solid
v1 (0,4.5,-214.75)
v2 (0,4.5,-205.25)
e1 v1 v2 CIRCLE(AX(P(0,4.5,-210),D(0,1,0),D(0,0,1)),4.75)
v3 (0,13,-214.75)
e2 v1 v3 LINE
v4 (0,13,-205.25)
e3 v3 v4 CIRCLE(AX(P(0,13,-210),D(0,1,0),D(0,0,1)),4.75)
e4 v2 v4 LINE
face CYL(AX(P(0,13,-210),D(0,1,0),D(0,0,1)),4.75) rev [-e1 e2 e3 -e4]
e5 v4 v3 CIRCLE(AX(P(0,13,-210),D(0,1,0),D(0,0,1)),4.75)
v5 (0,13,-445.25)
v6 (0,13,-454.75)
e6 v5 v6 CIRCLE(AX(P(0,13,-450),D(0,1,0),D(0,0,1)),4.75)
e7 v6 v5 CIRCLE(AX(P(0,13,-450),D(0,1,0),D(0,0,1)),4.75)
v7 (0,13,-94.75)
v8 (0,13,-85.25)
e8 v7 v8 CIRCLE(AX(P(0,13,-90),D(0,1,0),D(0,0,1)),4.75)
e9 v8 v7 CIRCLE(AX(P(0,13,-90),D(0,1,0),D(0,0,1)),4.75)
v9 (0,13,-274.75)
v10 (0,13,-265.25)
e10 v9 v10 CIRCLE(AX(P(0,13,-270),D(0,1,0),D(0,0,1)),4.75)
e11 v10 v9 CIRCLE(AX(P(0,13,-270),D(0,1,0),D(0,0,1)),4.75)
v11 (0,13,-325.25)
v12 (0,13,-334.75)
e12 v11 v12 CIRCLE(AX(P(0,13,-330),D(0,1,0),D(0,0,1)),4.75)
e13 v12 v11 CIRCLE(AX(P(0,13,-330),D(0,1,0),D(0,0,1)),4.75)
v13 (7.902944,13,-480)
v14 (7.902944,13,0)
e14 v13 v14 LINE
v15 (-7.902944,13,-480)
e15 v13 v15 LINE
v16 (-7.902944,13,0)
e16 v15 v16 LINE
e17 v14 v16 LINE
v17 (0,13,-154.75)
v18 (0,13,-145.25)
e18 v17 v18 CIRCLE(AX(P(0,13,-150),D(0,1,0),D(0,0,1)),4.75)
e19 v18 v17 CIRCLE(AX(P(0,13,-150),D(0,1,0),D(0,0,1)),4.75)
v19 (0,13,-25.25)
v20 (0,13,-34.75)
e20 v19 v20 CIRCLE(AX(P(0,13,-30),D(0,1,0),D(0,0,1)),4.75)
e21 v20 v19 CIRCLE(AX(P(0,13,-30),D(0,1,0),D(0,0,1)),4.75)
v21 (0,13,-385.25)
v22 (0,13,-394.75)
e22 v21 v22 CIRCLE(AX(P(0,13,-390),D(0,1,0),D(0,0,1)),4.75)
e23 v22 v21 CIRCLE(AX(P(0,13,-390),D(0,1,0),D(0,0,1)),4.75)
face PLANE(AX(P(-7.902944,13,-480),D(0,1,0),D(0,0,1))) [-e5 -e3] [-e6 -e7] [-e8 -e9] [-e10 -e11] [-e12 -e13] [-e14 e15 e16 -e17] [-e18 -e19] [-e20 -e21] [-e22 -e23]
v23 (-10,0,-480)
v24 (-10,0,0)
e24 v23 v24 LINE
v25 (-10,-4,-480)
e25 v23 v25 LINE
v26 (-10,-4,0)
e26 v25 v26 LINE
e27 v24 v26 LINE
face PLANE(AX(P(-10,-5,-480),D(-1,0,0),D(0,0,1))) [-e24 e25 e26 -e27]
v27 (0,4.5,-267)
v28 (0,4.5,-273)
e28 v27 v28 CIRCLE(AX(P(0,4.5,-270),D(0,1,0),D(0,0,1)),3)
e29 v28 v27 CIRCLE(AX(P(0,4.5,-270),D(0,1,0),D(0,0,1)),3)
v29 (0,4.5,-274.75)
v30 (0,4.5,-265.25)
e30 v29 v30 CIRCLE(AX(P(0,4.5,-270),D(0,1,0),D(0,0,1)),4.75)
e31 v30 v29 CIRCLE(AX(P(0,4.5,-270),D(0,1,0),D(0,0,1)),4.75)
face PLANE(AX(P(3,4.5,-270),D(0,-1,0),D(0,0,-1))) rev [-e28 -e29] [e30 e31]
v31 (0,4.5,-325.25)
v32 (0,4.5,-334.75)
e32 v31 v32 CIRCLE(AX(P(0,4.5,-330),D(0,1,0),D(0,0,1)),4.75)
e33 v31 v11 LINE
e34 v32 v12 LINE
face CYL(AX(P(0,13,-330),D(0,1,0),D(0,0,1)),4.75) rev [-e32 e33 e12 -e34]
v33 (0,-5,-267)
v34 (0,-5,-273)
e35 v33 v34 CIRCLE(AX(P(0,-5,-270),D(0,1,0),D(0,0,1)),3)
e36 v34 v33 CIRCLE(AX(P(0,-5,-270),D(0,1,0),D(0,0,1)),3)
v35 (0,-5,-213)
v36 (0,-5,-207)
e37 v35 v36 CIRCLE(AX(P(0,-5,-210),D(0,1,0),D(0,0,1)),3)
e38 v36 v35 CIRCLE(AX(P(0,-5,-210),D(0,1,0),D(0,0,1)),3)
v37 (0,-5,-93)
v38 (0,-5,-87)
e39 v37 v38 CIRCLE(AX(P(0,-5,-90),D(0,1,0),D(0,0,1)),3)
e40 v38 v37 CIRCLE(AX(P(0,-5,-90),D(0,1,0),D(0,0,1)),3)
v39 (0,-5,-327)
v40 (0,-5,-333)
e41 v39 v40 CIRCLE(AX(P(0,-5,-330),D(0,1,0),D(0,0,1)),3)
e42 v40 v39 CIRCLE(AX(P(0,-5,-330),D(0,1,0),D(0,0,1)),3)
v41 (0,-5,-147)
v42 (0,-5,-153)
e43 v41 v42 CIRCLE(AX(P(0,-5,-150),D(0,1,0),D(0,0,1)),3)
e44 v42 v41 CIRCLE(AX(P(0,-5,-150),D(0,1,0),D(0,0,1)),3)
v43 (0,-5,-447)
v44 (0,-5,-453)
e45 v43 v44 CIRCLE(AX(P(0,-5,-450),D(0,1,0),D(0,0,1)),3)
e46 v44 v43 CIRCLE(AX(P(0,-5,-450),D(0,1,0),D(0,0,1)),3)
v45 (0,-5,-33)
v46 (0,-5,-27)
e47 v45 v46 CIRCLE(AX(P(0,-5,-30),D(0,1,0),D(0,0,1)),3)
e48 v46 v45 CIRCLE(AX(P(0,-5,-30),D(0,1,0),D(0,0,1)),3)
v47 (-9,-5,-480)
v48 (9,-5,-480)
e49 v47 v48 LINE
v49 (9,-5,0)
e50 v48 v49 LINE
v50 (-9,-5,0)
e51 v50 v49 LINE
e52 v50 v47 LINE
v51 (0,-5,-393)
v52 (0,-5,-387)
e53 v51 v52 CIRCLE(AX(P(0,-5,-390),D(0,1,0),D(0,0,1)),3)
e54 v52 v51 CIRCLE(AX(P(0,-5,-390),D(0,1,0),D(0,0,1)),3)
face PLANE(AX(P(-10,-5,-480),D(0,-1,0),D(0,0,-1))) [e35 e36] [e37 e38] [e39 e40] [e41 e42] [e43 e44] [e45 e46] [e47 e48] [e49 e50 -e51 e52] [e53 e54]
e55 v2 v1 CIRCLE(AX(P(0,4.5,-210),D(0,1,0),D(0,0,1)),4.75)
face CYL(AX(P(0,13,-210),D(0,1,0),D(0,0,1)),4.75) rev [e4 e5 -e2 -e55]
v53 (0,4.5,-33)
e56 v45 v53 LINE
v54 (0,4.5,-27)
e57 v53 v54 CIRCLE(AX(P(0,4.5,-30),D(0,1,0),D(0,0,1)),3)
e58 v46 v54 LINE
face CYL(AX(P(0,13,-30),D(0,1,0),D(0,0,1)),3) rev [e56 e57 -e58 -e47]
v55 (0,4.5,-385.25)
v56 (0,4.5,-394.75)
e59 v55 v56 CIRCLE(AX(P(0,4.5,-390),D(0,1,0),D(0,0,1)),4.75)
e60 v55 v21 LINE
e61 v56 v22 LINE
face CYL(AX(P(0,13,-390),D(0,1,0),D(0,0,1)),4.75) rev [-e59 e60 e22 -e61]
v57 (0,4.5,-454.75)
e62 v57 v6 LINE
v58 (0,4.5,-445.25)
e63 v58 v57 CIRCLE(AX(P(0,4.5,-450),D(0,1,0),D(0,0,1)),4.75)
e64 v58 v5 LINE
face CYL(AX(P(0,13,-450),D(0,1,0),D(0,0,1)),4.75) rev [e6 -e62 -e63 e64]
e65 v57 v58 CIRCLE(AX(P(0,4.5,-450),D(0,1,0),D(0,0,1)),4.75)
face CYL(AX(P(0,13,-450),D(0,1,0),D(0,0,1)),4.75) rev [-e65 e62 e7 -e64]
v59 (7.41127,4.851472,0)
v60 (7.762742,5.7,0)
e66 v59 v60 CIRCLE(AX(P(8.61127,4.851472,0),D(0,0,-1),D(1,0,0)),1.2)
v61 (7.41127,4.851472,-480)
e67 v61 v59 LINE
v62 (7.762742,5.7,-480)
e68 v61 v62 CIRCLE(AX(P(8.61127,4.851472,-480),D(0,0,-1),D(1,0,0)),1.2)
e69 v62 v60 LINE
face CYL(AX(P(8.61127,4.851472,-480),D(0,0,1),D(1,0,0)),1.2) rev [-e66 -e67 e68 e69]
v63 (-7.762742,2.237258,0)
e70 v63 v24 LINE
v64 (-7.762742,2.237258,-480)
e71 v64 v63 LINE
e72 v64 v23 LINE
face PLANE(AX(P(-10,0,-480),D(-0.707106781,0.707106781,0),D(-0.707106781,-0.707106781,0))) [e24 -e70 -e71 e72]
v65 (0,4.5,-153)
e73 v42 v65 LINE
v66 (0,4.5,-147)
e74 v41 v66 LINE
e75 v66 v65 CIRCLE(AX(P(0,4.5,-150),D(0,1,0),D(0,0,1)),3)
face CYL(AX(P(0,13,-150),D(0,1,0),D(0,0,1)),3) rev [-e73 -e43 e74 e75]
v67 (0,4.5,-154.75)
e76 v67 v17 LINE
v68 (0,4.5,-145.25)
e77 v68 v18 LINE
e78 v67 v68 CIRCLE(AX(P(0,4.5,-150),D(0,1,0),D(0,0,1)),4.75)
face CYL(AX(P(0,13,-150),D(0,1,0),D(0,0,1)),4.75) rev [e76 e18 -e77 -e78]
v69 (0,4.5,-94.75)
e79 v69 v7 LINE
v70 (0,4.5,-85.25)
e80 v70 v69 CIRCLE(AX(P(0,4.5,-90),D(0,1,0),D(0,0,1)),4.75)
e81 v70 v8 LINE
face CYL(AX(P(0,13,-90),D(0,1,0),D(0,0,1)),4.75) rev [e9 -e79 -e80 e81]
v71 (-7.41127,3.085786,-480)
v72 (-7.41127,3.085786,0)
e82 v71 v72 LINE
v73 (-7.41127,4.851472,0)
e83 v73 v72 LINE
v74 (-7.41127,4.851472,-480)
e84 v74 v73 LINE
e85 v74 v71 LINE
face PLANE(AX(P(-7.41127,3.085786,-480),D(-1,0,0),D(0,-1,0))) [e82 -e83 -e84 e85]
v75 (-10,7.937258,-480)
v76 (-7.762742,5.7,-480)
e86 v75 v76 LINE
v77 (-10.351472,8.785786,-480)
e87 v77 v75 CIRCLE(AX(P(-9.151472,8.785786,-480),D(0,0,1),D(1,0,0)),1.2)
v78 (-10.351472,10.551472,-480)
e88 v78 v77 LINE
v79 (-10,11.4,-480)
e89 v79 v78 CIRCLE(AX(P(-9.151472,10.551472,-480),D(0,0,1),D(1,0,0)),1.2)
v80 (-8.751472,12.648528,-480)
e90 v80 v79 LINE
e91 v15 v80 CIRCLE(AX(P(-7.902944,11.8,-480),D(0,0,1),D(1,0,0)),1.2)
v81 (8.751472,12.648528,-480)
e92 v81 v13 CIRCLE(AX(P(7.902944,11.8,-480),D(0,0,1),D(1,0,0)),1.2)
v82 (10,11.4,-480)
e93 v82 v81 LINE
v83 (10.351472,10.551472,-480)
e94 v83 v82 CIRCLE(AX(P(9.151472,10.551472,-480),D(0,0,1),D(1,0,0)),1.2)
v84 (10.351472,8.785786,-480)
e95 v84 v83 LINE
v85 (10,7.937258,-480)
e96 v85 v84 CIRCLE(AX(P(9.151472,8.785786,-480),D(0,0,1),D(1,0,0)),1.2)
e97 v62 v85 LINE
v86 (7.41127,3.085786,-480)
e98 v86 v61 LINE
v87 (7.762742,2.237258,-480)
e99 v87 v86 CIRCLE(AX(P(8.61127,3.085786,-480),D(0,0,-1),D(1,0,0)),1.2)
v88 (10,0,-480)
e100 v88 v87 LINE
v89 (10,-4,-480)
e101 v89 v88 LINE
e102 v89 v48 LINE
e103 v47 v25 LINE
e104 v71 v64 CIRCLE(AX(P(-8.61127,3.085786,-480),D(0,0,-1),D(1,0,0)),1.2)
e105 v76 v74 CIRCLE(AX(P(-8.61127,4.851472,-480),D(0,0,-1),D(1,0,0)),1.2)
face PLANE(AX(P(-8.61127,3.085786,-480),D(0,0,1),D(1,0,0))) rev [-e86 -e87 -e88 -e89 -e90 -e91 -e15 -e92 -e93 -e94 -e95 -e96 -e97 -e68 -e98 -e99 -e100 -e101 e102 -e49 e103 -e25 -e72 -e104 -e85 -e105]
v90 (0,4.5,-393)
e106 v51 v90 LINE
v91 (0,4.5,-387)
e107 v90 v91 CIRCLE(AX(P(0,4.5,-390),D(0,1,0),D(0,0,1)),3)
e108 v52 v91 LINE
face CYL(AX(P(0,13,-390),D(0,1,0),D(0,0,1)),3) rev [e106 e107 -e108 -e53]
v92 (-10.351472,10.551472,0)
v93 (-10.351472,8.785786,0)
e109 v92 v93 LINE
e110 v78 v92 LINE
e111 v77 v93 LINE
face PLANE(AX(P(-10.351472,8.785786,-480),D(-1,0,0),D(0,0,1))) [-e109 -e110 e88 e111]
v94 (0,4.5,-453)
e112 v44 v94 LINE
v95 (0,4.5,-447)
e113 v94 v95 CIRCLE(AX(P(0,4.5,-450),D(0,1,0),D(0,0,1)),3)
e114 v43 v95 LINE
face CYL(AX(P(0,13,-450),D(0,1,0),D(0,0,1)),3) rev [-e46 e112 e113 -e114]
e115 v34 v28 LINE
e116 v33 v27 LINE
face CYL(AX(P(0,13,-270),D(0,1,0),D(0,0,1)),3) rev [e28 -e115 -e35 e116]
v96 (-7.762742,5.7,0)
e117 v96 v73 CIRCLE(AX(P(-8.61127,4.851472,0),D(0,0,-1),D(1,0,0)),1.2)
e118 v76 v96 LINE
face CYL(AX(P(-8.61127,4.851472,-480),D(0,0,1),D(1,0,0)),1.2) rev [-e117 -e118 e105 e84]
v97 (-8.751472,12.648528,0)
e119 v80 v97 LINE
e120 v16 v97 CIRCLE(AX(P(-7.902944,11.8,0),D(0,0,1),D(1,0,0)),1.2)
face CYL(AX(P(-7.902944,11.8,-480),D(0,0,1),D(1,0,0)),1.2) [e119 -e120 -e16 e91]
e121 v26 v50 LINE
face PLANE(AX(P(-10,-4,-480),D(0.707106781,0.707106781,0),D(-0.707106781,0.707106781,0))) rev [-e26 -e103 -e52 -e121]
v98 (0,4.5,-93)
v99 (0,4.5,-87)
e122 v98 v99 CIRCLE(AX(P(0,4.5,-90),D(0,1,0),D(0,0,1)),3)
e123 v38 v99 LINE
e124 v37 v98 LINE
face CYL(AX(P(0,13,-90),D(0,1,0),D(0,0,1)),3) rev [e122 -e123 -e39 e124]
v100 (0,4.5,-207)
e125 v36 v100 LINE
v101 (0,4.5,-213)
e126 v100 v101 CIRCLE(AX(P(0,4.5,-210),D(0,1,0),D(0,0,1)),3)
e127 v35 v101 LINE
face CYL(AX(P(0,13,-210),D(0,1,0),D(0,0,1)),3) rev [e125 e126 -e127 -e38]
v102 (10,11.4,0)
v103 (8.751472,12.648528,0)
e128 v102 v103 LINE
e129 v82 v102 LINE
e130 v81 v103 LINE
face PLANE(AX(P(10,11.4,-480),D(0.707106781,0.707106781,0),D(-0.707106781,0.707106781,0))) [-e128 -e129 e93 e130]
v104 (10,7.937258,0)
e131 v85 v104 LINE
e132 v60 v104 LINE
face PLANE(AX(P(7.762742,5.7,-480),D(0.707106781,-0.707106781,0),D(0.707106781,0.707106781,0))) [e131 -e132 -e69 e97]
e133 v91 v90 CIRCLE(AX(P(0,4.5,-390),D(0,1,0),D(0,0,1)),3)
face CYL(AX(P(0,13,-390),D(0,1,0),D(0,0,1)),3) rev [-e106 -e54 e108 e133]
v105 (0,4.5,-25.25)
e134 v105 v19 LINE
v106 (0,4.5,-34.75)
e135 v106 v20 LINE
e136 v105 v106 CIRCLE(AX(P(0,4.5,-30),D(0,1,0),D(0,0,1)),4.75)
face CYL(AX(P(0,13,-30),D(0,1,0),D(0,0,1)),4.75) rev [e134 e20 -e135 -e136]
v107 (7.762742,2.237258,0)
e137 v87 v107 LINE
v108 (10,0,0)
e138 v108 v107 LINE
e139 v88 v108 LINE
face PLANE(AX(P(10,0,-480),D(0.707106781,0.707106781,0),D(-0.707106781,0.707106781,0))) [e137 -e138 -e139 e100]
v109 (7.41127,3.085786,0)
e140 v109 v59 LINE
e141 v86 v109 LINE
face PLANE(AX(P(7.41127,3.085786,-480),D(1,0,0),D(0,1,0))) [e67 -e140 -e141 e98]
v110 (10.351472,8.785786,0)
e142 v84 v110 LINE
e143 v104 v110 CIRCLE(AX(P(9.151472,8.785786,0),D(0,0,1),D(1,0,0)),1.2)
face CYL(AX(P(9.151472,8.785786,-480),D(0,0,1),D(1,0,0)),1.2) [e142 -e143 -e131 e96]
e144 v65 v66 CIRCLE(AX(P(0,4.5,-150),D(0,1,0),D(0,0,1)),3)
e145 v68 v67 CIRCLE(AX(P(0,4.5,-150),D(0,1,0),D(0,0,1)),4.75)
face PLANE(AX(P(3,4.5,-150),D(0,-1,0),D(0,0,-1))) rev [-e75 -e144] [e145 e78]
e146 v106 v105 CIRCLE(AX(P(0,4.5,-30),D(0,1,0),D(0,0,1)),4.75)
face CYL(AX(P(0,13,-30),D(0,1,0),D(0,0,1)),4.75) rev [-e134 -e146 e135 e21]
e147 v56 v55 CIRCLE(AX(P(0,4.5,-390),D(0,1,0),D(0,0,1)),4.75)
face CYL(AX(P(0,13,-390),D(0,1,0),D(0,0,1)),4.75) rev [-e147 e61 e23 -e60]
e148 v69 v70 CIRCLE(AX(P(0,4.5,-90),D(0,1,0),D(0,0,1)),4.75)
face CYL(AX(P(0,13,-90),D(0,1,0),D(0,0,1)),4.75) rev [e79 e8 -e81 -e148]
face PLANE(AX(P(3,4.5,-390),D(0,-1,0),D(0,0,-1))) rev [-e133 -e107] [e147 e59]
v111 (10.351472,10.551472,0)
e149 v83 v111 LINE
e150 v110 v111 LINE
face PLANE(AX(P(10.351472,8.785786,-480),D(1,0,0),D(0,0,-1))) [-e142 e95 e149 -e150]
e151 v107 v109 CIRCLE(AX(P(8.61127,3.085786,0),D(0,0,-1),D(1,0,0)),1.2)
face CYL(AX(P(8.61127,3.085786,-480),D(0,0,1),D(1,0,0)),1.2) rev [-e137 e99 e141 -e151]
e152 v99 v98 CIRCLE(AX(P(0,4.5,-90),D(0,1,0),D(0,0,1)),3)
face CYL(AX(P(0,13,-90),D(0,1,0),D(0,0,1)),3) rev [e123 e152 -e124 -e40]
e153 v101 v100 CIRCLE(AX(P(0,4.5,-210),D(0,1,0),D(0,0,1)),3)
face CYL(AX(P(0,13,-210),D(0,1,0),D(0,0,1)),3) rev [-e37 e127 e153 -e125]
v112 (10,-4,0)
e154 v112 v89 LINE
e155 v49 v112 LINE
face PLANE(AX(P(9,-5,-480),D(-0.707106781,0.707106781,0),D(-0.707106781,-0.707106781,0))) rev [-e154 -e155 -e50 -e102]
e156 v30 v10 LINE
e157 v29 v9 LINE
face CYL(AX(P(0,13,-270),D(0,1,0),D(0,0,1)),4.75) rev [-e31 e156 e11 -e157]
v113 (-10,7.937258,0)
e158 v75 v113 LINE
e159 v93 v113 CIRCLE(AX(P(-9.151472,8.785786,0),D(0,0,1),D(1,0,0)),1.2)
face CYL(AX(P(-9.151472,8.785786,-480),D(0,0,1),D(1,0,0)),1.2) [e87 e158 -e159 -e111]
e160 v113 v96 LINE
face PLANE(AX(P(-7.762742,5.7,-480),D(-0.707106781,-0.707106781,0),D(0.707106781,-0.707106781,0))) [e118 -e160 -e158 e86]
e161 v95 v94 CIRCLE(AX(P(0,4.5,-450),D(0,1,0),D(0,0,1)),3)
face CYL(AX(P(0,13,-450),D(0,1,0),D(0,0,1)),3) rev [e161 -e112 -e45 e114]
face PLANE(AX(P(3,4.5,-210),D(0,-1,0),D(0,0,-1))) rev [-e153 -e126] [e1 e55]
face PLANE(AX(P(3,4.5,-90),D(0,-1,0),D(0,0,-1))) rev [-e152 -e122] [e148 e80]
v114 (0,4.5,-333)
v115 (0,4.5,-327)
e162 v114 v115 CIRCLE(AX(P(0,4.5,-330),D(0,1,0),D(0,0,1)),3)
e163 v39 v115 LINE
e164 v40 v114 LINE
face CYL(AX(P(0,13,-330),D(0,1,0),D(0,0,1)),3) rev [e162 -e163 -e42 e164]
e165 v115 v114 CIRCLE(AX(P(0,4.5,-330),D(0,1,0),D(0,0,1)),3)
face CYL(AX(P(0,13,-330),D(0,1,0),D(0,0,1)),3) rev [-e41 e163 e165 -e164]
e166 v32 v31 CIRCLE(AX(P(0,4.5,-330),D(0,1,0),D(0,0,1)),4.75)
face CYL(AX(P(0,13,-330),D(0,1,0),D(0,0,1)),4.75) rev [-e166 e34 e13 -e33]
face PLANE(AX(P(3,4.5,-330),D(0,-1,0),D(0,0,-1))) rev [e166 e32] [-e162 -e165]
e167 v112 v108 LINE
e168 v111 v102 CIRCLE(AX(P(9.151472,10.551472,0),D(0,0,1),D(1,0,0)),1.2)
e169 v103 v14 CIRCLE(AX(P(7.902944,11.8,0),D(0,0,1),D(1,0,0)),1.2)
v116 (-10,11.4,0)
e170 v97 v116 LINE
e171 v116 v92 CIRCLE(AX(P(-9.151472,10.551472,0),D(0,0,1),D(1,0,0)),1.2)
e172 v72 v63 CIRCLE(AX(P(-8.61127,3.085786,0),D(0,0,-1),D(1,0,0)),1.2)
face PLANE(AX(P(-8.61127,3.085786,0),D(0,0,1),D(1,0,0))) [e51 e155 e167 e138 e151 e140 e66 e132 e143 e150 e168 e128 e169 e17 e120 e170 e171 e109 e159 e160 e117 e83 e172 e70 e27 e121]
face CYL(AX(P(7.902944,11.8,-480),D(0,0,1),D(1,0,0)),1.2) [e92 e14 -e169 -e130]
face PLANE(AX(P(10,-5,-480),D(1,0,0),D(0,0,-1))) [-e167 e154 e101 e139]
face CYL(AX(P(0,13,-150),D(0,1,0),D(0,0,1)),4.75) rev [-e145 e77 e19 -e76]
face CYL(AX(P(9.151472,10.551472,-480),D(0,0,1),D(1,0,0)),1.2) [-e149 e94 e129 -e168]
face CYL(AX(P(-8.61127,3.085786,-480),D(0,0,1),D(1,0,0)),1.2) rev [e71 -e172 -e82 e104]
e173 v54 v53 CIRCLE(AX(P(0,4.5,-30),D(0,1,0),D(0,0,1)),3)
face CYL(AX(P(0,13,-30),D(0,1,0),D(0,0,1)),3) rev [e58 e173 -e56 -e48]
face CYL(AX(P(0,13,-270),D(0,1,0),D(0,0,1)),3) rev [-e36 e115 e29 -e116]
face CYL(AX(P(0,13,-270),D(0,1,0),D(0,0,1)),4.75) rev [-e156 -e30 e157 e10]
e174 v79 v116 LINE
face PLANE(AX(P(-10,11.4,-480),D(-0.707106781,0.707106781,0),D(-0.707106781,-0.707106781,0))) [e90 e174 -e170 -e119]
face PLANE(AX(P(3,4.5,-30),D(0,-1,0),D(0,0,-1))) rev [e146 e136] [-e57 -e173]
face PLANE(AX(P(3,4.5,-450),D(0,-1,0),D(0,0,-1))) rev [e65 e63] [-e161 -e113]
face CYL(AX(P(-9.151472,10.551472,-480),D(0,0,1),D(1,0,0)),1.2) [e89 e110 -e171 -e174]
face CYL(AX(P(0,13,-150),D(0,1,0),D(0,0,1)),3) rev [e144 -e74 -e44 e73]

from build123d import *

# Parameters (mm, degrees)
BOSS_EXTRUDE1_DEPTH           = 480
COUNTERSINK_HOLE1_D           = 6
COUNTERSINK_HOLE1_CBORE_D     = 9.5
COUNTERSINK_HOLE1_CBORE_DEPTH = 8.5
LPATTERN1_COUNT               = 8
LPATTERN1_PITCH               = 60
CHAMFER1_SIZE                 = 1


with BuildPart() as part:
    # Sketch3 → Boss-Extrude1 (new body)
    with BuildSketch(Plane.XY):
        with BuildLine():
            Line((-10, -5), (10, -5))
            Line((10, -5), (10, 0))
            Line((10, 0), (7.7627417, 2.2372583))
            ThreePointArc((7.7627417, 2.2372583), (7.502614398, 2.626566319), (7.411269837, 3.085786438))
            Line((7.411269837, 3.085786438), (7.411269837, 4.851471863))
            ThreePointArc((7.411269837, 4.851471863), (7.502614398, 5.310691981), (7.7627417, 5.7))
            Line((7.7627417, 5.7), (10, 7.9372583))
            ThreePointArc((10, 7.9372583), (10.260127302, 8.326566319), (10.351471863, 8.785786438))
            Line((10.351471863, 8.785786438), (10.351471863, 10.551471863))
            ThreePointArc((10.351471863, 10.551471863), (10.260127302, 11.010691981), (10, 11.4))
            Line((10, 11.4), (8.751471863, 12.648528137))
            ThreePointArc((8.751471863, 12.648528137), (8.362163844, 12.908655439), (7.902943725, 13))
            Line((7.902943725, 13), (-7.902943725, 13))
            ThreePointArc((-7.902943725, 13), (-8.362163844, 12.908655439), (-8.751471863, 12.648528137))
            Line((-8.751471863, 12.648528137), (-10, 11.4))
            ThreePointArc((-10, 11.4), (-10.260127302, 11.010691981), (-10.351471863, 10.551471863))
            Line((-10.351471863, 10.551471863), (-10.351471863, 8.785786438))
            ThreePointArc((-10.351471863, 8.785786438), (-10.260127302, 8.326566319), (-10, 7.9372583))
            Line((-10, 7.9372583), (-7.7627417, 5.7))
            ThreePointArc((-7.7627417, 5.7), (-7.502614398, 5.310691981), (-7.411269837, 4.851471863))
            Line((-7.411269837, 4.851471863), (-7.411269837, 3.085786438))
            ThreePointArc((-7.411269837, 3.085786438), (-7.502614398, 2.626566319), (-7.7627417, 2.2372583))
            Line((-7.7627417, 2.2372583), (-10, 0))
            Line((-10, 0), (-10, -5))
        make_face()
    extrude(amount=-BOSS_EXTRUDE1_DEPTH)

    # Countersink Hole1 (through all)
    with Locations(Plane(origin=(0, 13, 0), x_dir=(-1, 0, 0), z_dir=(0, 1, 0))):
        with Locations((0, -30)):
            countersink_hole1 = CounterBoreHole(COUNTERSINK_HOLE1_D / 2, COUNTERSINK_HOLE1_CBORE_D / 2, COUNTERSINK_HOLE1_CBORE_DEPTH)

    # LPattern1: Countersink Hole1 ×8
    with Locations(*[(0, 0, -i * LPATTERN1_PITCH) for i in range(1, LPATTERN1_COUNT)]):
        add(countersink_hole1, mode=Mode.SUBTRACT)

    # Chamfer1
    chamfer1_edges = [part.edges().sort_by_distance(p)[0] for p in [
        (10, -5, -240),
        (-10, -5, -240),
    ]]
    chamfer(chamfer1_edges, length=CHAMFER1_SIZE)


solid = part.part
